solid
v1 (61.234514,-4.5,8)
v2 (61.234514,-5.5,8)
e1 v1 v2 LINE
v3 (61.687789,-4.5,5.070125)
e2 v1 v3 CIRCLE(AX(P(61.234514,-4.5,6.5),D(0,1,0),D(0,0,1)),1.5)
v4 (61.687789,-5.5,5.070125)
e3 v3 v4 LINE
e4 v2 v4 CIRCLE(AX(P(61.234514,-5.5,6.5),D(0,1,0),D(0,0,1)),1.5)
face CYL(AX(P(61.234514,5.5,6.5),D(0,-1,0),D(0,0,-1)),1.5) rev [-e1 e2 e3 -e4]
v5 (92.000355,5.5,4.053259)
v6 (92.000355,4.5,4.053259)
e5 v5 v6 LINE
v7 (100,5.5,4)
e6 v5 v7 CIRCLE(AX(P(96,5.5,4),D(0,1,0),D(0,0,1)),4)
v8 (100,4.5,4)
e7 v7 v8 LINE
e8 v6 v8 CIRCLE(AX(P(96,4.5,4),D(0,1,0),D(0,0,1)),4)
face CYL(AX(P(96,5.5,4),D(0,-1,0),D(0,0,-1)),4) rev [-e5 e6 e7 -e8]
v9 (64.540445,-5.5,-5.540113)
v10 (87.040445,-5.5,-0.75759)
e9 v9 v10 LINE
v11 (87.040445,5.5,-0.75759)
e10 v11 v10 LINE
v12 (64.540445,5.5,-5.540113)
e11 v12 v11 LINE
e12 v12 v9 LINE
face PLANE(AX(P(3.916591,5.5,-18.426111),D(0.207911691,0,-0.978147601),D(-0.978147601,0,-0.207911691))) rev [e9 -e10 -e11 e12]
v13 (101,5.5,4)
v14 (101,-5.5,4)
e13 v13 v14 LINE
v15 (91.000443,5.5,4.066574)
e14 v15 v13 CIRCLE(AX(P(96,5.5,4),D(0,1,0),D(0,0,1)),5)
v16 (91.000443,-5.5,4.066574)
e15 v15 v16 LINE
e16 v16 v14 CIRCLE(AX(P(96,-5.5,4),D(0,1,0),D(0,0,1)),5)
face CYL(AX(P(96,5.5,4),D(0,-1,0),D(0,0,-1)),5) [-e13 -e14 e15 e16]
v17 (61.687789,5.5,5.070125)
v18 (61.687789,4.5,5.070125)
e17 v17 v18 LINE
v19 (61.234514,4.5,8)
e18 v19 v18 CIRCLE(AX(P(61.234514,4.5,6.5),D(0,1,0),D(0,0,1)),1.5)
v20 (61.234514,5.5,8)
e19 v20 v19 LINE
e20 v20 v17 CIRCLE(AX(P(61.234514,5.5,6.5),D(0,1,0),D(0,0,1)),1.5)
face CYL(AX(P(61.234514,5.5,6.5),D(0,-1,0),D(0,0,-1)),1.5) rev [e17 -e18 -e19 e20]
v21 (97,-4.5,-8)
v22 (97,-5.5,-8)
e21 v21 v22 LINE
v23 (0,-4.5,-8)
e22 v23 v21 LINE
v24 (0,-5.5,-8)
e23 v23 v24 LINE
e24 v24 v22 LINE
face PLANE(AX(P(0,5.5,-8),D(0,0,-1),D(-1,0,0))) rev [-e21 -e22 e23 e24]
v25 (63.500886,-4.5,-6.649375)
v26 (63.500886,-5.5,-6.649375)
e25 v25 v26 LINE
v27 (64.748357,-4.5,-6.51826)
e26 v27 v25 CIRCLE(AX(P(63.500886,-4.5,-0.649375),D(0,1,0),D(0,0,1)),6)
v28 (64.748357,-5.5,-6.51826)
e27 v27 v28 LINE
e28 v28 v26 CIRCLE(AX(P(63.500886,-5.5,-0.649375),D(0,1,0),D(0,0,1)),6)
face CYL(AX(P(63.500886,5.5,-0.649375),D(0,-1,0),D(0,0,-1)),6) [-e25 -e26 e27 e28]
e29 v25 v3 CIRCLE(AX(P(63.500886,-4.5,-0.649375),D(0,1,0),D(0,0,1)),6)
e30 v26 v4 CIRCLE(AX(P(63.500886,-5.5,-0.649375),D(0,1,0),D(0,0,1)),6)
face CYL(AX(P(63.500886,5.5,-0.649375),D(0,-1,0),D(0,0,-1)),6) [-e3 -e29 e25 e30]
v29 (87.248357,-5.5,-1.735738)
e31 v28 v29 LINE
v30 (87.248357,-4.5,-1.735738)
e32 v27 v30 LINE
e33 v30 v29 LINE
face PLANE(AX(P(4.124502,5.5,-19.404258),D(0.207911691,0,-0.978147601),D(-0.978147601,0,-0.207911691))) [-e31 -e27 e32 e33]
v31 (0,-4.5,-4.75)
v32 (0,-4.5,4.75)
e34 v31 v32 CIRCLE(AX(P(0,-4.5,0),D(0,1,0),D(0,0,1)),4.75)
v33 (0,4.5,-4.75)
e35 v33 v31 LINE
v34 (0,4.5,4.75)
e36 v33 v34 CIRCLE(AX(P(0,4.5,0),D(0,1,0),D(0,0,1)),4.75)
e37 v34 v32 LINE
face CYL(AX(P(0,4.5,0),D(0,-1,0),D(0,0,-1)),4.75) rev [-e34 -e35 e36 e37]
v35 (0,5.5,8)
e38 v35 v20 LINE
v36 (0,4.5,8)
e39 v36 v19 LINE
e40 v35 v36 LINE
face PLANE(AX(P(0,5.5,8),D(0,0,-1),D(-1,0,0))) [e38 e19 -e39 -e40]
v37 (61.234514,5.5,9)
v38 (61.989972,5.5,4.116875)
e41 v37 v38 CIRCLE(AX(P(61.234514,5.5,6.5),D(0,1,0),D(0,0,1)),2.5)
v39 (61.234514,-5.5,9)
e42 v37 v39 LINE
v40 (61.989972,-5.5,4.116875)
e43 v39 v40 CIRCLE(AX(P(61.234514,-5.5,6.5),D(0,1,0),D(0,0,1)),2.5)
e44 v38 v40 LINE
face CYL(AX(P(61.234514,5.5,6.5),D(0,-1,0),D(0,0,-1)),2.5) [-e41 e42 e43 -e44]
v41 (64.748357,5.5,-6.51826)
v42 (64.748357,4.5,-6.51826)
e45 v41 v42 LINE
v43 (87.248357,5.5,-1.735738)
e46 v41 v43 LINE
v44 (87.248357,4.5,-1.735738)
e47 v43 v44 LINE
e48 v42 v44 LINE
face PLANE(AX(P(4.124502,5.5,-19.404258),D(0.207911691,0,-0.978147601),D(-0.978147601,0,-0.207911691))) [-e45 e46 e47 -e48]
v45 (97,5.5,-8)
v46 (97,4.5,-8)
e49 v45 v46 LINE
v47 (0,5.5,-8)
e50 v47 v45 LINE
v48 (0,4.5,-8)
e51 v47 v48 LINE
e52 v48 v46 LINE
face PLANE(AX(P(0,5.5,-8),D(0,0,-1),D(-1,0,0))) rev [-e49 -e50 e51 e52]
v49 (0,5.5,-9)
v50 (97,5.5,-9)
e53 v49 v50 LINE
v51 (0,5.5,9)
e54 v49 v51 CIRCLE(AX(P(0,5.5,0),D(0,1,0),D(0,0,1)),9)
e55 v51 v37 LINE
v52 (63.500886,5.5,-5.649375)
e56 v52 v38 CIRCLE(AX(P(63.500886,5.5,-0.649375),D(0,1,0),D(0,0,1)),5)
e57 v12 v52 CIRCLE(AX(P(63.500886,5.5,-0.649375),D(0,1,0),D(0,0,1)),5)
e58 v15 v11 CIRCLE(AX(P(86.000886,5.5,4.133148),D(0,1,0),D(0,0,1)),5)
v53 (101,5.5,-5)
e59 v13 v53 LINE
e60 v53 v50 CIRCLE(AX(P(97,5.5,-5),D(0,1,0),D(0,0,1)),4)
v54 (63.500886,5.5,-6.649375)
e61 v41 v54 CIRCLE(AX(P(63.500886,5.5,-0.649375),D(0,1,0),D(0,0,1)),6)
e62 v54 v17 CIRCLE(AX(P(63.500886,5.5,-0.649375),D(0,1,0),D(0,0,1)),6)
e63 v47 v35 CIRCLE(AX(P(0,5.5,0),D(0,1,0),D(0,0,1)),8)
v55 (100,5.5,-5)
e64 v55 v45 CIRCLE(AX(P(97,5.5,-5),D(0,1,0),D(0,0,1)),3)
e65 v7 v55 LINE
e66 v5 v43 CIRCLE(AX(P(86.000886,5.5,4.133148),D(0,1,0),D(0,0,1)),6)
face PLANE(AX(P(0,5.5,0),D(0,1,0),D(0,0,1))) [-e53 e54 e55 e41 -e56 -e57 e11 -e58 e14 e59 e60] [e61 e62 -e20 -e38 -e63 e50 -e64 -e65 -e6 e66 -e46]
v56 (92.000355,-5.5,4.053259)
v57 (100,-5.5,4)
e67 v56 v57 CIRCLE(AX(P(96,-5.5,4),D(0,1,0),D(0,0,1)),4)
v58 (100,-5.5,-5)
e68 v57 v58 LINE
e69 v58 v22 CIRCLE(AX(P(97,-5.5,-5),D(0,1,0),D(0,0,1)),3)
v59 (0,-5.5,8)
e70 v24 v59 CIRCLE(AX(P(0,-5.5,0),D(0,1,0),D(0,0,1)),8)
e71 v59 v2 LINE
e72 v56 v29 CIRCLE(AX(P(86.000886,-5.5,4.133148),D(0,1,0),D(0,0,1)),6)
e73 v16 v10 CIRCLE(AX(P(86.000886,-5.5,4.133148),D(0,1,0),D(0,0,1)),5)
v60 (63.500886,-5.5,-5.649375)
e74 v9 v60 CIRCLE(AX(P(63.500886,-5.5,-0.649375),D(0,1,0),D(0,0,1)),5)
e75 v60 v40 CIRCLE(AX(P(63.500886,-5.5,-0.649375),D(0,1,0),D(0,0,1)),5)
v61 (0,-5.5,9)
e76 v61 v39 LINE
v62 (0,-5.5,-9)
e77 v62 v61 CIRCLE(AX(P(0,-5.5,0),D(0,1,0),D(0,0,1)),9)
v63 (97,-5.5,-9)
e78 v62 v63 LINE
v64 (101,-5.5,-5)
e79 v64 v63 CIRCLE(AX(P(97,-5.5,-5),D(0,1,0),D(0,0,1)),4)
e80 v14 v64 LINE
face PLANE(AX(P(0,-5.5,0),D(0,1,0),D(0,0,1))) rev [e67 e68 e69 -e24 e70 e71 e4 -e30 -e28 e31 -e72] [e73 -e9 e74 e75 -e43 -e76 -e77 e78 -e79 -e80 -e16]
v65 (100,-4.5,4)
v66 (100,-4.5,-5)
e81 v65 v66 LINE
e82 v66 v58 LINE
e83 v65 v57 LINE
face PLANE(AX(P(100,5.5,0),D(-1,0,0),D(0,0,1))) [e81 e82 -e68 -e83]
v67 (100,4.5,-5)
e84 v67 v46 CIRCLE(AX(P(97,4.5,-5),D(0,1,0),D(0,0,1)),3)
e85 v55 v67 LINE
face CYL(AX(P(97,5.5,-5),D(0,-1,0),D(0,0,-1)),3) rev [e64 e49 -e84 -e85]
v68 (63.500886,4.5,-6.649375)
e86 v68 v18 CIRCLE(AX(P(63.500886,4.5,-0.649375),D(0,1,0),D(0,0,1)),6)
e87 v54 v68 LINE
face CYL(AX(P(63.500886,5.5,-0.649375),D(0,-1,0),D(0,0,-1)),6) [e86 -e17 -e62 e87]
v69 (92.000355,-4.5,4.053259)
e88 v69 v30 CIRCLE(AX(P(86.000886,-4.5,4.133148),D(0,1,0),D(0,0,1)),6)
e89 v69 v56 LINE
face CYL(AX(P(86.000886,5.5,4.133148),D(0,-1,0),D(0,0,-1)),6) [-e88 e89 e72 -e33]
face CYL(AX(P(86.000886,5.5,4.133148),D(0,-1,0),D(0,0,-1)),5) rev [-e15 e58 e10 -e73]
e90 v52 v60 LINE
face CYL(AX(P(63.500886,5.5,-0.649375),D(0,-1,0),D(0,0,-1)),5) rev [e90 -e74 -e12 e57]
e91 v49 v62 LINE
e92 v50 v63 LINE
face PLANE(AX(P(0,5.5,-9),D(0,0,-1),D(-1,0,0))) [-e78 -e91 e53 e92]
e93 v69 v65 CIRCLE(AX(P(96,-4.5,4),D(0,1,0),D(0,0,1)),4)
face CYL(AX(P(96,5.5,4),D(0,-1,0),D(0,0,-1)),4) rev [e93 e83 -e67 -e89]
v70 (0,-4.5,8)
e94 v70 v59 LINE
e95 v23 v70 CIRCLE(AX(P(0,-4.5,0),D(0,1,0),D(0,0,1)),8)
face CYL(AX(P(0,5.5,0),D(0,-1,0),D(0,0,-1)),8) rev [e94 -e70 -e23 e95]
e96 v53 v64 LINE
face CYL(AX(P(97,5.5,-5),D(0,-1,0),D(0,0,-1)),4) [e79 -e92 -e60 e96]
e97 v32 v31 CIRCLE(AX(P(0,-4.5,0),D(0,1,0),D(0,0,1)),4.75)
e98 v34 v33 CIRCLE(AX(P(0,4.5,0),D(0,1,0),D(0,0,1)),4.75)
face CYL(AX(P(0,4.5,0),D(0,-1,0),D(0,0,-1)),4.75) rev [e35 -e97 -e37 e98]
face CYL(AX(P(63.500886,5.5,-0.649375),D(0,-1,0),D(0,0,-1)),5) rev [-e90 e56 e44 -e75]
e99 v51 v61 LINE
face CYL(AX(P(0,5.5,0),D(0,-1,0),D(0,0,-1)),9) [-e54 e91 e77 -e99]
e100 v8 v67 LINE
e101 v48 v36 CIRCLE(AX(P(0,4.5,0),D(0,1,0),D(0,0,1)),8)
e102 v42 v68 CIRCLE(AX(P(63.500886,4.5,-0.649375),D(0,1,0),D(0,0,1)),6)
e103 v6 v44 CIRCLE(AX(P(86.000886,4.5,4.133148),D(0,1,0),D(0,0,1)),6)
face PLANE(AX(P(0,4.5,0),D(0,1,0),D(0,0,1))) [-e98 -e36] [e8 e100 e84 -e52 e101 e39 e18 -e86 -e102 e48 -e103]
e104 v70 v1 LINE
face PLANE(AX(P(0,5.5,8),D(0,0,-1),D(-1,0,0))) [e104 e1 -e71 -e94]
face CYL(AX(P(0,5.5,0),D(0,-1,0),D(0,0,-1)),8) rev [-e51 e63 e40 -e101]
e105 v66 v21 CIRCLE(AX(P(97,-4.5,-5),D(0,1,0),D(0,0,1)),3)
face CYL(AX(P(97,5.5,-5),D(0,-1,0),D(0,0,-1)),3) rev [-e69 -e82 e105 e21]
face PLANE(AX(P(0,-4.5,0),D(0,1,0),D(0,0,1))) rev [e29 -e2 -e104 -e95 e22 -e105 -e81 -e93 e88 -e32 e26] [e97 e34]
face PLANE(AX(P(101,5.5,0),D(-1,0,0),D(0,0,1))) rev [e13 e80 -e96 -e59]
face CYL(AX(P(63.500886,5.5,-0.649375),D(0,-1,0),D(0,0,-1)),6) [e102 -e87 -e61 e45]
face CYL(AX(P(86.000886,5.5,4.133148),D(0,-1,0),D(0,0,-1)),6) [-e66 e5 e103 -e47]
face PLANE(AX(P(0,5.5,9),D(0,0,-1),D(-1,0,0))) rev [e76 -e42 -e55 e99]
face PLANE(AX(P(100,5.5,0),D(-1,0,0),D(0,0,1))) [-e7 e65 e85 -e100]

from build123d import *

# Parameters (mm, degrees)
OPENER_PROFILE_SKETCH_R = 4.75
OPENER_BODY_9MM_DEPTH   = 4.5
RAISED_RIM_11MM_DEPTH   = 5.5


with BuildPart() as part:
    # Opener Profile Sketch → Opener Body 9mm (new, symmetric)
    with BuildSketch(Plane(origin=(0, 0, 0), x_dir=(1, 0, 0), z_dir=(0, 1, 0))):
        with BuildLine():
            ThreePointArc((92.000354584, -4.053259235), (90.638520492, -0.326266085), (87.248356605, 1.735737516))
            Line((87.248356605, 1.735737516), (64.748356605, 6.518260154))
            ThreePointArc((64.748356605, 6.518260154), (57.699795888, 2.181480349), (61.687788593, -5.07012509))
            ThreePointArc((61.687788593, -5.07012509), (62.71687919, -6.72933342), (61.234514126, -8))
            Line((61.234514126, -8), (0, -8))
            ThreePointArc((0, -8), (-8, 0), (0, 8))
            Line((0, 8), (97, 8))
            ThreePointArc((97, 8), (99.121320344, 7.121320344), (100, 5))
            Line((100, 5), (100, -4))
            ThreePointArc((100, -4), (96.026630208, -7.999911353), (92.000354584, -4.053259235))
        make_face()
        with Locations(Location((0, 0, 0), (0, 0, 270))):
            Circle(OPENER_PROFILE_SKETCH_R, mode=Mode.SUBTRACT)
    extrude(amount=OPENER_BODY_9MM_DEPTH, both=True)

    # Sketch1_3 → Raised Rim 11mm (add, symmetric)
    with BuildSketch(Plane(origin=(0, 0, 0), x_dir=(1, 0, 0), z_dir=(0, 1, 0))):
        with BuildLine():
            ThreePointArc((91.00044323, -4.066574044), (89.865581487, -0.960746419), (87.040444914, 0.757589915))
            Line((87.040444914, 0.757589915), (64.540444914, 5.540112553))
            ThreePointArc((64.540444914, 5.540112553), (58.666644317, 1.926129382), (61.989971571, -4.11687515))
            ThreePointArc((61.989971571, -4.11687515), (63.705122566, -6.882222367), (61.234514126, -9))
            Line((61.234514126, -9), (0, -9))
            ThreePointArc((0, -9), (-9, 0), (0, 9))
            Line((0, 9), (97, 9))
            ThreePointArc((97, 9), (99.828427125, 7.828427125), (101, 5))
            Line((101, 5), (101, -4))
            ThreePointArc((101, -4), (96.03328776, -8.999889191), (91.00044323, -4.066574044))
        make_face()
        with BuildLine():
            ThreePointArc((92.000354584, -4.053259235), (96.026630208, -7.999911353), (100, -4))
            Line((100, -4), (100, 5))
            ThreePointArc((100, 5), (99.121320344, 7.121320344), (97, 8))
            Line((97, 8), (0, 8))
            ThreePointArc((0, 8), (-8, 0), (0, -8))
            Line((0, -8), (61.234514126, -8))
            ThreePointArc((61.234514126, -8), (62.71687919, -6.72933342), (61.687788593, -5.07012509))
            ThreePointArc((61.687788593, -5.07012509), (57.699795888, 2.181480349), (64.748356605, 6.518260154))
            Line((64.748356605, 6.518260154), (87.248356605, 1.735737516))
            ThreePointArc((87.248356605, 1.735737516), (90.638520492, -0.326266085), (92.000354584, -4.053259235))
        make_face(mode=Mode.SUBTRACT)
    extrude(amount=RAISED_RIM_11MM_DEPTH, both=True)


solid = part.part
